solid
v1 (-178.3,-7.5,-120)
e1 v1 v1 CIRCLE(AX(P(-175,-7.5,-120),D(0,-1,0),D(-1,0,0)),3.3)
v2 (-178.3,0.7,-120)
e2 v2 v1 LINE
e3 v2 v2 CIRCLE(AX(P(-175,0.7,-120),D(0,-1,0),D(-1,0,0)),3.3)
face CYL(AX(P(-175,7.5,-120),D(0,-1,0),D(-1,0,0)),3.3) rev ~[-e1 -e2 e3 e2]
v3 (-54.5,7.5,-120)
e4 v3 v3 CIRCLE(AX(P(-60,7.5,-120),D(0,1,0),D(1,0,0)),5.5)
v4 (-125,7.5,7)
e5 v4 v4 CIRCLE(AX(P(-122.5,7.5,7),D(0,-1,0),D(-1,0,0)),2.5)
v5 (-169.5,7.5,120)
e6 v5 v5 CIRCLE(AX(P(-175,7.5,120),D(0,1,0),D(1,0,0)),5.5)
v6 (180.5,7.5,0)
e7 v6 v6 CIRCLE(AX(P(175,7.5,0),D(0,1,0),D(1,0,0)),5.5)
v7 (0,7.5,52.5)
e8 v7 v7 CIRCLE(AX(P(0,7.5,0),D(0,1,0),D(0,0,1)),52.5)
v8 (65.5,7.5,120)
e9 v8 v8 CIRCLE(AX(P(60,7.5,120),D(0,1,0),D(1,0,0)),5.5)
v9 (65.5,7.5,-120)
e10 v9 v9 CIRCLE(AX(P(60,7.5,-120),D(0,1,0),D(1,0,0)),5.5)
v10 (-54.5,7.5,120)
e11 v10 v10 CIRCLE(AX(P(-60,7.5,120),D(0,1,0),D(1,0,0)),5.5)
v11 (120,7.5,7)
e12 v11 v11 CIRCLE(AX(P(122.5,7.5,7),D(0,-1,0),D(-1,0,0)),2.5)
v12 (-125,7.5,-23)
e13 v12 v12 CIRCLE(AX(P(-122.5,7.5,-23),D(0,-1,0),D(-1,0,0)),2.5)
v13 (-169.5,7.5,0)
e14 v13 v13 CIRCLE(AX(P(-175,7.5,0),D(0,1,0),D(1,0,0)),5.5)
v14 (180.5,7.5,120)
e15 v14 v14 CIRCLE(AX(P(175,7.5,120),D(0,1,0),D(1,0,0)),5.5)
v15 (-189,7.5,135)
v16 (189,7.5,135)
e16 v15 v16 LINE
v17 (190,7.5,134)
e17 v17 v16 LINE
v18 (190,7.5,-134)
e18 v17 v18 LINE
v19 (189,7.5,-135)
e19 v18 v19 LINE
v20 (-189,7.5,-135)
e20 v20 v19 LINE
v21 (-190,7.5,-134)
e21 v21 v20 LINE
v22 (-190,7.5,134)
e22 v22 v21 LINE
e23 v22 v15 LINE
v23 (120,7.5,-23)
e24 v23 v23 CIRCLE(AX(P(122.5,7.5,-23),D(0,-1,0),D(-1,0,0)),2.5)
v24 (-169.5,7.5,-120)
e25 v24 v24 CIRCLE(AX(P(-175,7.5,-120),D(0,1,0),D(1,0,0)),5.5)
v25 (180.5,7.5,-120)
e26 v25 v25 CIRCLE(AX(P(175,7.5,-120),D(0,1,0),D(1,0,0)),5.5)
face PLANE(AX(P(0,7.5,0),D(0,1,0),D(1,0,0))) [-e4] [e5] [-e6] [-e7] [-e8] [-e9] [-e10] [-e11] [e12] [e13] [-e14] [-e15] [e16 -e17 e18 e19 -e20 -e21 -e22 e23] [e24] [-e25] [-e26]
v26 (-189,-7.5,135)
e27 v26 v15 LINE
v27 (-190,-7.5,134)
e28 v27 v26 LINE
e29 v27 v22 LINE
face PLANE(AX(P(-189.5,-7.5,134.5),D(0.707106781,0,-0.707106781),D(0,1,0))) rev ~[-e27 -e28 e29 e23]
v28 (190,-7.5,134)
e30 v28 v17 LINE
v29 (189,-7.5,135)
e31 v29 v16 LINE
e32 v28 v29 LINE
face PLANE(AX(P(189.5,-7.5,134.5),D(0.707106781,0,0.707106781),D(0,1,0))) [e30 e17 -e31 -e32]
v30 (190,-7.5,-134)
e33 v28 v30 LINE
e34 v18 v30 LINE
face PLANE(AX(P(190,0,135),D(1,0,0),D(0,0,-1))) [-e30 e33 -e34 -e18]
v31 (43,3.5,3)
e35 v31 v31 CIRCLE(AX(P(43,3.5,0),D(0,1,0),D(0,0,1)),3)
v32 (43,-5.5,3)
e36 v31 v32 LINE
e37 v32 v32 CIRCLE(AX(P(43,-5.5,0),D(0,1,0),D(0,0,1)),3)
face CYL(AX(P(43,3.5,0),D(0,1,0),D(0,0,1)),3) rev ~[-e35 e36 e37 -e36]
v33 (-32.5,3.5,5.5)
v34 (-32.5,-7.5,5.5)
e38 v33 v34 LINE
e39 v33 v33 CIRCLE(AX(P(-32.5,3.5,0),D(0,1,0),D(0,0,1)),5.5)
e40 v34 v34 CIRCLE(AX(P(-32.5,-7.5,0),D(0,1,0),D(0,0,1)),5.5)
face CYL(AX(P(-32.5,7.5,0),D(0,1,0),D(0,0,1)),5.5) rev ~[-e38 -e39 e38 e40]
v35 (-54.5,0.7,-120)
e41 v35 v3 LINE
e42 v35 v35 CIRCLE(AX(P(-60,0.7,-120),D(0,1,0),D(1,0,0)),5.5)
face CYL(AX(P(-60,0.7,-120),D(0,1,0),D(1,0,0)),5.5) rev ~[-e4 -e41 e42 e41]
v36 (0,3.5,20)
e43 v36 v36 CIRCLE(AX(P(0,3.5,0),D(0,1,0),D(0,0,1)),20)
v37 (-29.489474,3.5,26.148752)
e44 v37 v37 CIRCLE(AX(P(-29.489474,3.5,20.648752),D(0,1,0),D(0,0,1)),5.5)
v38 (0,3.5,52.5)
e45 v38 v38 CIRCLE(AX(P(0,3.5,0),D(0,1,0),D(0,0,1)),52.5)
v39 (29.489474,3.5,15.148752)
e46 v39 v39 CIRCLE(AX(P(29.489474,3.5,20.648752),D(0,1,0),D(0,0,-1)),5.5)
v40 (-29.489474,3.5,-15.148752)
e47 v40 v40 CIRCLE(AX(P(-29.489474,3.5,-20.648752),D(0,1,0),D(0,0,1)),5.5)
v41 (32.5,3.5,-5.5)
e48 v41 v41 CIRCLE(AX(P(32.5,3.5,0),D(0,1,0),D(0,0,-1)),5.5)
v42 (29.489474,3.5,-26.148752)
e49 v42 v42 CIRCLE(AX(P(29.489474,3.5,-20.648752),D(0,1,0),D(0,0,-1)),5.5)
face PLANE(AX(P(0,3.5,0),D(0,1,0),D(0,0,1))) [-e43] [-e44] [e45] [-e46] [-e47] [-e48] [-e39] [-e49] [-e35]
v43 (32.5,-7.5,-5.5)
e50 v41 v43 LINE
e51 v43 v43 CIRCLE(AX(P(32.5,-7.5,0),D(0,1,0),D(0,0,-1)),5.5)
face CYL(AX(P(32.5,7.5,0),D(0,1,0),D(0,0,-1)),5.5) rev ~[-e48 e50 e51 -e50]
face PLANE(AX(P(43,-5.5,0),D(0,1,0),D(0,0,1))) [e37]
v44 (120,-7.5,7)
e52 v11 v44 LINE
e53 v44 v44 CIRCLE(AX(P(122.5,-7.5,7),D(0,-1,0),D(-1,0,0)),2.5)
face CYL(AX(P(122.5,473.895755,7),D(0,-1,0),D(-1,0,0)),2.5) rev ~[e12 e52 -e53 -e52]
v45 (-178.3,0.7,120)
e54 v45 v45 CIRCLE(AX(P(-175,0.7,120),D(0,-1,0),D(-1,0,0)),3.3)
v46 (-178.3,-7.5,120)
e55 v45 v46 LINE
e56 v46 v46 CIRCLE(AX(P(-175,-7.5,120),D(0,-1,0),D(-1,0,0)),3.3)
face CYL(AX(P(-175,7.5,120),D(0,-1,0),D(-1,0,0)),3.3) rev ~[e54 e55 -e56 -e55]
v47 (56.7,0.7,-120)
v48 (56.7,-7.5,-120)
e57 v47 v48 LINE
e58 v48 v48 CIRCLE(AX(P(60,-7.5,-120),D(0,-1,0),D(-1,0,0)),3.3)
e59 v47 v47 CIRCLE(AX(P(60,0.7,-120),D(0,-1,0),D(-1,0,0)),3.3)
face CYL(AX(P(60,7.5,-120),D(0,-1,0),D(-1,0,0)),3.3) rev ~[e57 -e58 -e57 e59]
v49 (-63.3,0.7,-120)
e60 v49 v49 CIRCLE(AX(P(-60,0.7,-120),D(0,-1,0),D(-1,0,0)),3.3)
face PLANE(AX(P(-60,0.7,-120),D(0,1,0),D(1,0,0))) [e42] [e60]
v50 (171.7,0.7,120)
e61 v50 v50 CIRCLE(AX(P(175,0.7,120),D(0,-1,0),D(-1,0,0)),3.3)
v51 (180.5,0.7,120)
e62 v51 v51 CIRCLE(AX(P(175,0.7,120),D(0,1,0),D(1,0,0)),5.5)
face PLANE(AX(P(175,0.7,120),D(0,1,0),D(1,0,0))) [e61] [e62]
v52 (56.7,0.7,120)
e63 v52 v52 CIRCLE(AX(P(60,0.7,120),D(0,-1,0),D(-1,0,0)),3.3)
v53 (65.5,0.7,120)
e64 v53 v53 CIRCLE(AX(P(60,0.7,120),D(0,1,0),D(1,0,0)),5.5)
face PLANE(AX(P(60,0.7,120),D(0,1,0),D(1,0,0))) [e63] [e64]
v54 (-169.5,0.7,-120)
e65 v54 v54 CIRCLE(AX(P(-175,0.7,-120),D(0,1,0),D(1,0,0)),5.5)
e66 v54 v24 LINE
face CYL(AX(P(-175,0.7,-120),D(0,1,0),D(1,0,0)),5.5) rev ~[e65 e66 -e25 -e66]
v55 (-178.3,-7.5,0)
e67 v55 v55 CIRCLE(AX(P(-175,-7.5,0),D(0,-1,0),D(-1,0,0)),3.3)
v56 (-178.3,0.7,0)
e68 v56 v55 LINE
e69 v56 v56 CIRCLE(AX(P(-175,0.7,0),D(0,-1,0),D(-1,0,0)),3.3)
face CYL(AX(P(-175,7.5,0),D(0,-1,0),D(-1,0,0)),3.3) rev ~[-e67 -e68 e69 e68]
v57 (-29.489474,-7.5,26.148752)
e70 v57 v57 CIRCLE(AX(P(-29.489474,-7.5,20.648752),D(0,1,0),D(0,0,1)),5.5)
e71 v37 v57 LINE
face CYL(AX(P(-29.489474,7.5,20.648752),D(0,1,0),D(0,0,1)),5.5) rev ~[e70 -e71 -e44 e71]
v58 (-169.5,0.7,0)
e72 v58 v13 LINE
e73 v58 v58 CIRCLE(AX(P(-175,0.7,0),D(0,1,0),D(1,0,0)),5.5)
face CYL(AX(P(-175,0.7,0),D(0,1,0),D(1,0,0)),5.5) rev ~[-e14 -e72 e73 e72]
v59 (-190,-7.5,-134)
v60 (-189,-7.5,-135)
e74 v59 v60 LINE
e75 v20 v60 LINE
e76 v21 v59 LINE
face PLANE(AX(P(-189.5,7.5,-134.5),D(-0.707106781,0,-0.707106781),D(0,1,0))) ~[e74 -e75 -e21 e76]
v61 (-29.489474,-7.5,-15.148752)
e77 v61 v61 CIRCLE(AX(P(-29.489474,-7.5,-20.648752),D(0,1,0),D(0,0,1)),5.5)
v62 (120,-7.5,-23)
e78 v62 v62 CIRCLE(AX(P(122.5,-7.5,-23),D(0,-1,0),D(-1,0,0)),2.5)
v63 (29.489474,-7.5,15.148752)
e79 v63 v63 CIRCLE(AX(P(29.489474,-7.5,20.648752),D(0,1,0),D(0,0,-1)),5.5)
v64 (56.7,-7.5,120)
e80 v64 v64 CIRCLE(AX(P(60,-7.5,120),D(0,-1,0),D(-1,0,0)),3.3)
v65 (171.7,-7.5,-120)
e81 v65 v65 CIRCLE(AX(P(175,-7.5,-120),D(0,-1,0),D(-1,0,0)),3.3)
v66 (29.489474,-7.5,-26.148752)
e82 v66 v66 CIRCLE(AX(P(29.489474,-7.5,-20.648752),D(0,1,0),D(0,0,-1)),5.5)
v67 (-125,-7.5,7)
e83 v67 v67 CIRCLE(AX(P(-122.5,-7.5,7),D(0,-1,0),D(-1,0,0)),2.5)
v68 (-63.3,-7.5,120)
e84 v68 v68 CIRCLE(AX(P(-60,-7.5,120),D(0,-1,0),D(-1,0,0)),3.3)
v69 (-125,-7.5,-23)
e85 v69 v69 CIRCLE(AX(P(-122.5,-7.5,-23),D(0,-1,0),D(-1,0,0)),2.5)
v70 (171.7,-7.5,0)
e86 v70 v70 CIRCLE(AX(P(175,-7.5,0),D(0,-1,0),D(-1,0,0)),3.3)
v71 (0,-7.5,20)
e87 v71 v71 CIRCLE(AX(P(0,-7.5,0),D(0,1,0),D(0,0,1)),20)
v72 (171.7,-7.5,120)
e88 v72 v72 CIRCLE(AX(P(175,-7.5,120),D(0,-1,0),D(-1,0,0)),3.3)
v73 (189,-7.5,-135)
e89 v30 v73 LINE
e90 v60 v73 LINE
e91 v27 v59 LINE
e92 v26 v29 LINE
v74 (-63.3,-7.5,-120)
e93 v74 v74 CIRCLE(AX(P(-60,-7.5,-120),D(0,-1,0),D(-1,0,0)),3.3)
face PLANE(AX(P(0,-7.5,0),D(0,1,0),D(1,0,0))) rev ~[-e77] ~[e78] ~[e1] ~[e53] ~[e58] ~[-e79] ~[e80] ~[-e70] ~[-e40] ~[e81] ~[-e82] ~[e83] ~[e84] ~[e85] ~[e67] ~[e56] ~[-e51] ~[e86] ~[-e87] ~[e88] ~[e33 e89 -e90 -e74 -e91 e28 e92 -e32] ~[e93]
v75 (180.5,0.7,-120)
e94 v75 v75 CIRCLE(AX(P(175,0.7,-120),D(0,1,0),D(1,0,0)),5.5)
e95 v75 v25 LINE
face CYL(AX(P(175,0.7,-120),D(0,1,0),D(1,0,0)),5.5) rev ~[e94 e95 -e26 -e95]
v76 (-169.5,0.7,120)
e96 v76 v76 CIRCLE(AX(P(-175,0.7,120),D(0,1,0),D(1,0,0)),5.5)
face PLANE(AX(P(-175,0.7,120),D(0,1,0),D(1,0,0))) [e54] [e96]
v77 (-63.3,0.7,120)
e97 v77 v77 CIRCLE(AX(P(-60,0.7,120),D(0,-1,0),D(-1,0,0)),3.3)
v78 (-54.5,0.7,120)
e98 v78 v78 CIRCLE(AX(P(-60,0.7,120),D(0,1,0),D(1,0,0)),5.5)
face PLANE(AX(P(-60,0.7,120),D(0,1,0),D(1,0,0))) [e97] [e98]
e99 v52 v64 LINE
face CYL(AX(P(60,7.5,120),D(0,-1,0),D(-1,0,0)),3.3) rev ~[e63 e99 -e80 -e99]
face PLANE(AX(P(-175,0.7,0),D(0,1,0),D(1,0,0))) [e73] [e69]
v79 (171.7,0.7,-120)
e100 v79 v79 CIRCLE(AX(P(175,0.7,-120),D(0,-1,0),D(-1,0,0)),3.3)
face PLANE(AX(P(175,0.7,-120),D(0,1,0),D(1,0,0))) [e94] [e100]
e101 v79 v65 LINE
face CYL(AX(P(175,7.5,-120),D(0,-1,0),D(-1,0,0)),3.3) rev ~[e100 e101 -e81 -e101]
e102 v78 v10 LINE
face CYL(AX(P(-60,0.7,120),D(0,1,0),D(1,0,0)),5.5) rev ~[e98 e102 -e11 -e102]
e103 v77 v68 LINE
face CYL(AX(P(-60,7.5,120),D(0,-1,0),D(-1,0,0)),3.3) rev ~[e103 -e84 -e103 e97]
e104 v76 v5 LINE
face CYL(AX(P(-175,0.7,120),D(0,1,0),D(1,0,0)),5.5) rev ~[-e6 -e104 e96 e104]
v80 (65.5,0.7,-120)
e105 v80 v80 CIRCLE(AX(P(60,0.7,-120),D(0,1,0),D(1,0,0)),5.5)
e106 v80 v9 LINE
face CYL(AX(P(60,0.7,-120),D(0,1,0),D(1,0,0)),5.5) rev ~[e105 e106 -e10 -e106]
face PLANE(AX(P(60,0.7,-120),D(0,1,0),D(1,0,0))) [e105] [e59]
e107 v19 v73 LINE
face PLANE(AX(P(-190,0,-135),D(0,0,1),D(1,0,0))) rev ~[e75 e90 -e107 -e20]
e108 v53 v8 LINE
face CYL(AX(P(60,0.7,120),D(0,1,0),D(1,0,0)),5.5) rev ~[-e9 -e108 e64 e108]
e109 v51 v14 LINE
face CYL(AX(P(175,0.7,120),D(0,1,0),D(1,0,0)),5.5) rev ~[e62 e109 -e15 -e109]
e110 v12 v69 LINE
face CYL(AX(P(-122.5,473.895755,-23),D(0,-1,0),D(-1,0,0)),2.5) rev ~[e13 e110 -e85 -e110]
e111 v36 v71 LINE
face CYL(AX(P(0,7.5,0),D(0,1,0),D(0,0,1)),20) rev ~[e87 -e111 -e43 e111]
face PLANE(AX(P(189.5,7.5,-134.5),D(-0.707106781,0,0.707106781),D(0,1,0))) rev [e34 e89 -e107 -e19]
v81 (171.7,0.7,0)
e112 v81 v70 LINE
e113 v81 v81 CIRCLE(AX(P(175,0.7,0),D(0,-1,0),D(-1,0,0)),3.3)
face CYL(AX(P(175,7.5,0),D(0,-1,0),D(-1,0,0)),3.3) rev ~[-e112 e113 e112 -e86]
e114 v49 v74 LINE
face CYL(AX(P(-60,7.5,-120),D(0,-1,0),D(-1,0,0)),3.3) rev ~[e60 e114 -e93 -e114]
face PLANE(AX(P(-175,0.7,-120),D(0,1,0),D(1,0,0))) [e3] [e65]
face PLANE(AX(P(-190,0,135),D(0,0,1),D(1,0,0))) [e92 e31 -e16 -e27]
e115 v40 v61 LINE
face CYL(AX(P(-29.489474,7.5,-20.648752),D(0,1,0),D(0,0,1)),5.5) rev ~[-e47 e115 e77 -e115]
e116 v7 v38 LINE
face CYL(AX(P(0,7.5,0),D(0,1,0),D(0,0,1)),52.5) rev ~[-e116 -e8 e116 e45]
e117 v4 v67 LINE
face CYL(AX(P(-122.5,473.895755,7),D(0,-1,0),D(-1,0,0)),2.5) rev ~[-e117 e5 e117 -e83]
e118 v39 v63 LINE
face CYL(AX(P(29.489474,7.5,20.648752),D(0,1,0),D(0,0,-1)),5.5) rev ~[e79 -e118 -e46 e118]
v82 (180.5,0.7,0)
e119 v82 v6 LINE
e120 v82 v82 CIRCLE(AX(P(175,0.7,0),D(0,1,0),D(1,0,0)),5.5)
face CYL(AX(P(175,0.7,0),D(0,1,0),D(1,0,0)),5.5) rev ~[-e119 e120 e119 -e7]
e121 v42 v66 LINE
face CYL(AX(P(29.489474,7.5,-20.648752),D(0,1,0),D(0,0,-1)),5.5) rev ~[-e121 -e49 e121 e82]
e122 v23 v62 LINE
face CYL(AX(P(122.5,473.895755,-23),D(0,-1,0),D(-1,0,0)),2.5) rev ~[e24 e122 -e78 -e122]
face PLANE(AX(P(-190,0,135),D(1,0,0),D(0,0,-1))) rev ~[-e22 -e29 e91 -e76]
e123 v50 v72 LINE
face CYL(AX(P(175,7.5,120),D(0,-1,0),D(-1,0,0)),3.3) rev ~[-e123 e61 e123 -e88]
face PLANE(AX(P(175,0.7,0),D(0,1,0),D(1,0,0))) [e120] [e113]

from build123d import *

# Parameters (mm, degrees)
SKETCH_1_W                = 380
SKETCH_1_H                = 270
EXTRUDE_1_DEPTH           = 7.5
CHAMFER_1_SIZE            = 1
SKETCH_2_R                = 20
CUT_EXTRUDE_1_DEPTH       = 15
HOLE_WIZARD_3_D           = 6.6
HOLE_WIZARD_3_CBORE_D     = 11
HOLE_WIZARD_3_CBORE_DEPTH = 6.8
SKETCH_9_R                = 5.5
CUT_EXTRUDE_2_DEPTH       = 234.559414283
SKETCH_11_R               = 52.5
CUT_EXTRUDE_3_DEPTH       = 4
HOLE_WIZARD_M6_1_D        = 5
SKETCH_15_R               = 3
CUT_EXTRUDE_4_DEPTH       = 9


with BuildPart() as part:
    # 草图1 → 凸台-拉伸1 (new, symmetric)
    with BuildSketch(Plane(origin=(0, 0, 0), x_dir=(1, 0, 0), z_dir=(0, 1, 0))):
        Rectangle(SKETCH_1_W, SKETCH_1_H)
    extrude(amount=EXTRUDE_1_DEPTH, both=True)

    # 倒角1
    chamfer_1_edges = [part.edges().sort_by_distance(p)[0] for p in [
        (190, 0, 135),
        (-190, 0, 135),
        (-190, 0, -135),
        (190, 0, -135),
    ]]
    chamfer(chamfer_1_edges, length=CHAMFER_1_SIZE)

    # 草图2 → 切除-拉伸1 (cut)
    with BuildSketch(Plane(origin=(0, 7.5, 0), x_dir=(1, 0, 0), z_dir=(0, 1, 0))):
        with Locations(Location((0, 0, 0), (0, 0, 270))):
            Circle(SKETCH_2_R)
    extrude(amount=-CUT_EXTRUDE_1_DEPTH, mode=Mode.SUBTRACT)

    # 打孔尺寸(%根据)内六角圆柱头螺钉的类型3 (through all)
    with Locations(Plane(origin=(0, 7.5, 0), x_dir=(1, 0, 0), z_dir=(0, 1, 0))):
        with Locations((-175, 120), (-60, 120), (-60, -120), (-175, 0), (-175, -120), (175, -120), (175, 0), (60, -120), (60, 120), (175, 120)):
            CounterBoreHole(HOLE_WIZARD_3_D / 2, HOLE_WIZARD_3_CBORE_D / 2, HOLE_WIZARD_3_CBORE_DEPTH)

    # 草图9 → 切除-拉伸2 (cut, through all)
    with BuildSketch(Plane(origin=(0, 7.5, 0), x_dir=(1, 0, 0), z_dir=(0, 1, 0))):
        with Locations(Location((-29.489473594, 20.648751709, 0), (0, 0, 270))):
            Circle(SKETCH_9_R)
        with Locations(Location((-29.489473594, -20.648751709, 0), (0, 0, 270))):
            Circle(SKETCH_9_R)
        with Locations(Location((-32.5, 0, 0), (0, 0, 270))):
            Circle(SKETCH_9_R)
        with Locations(Location((29.489473594, -20.648751709, 0), (0, 0, 90))):
            Circle(SKETCH_9_R)
        with Locations(Location((32.5, 0, 0), (0, 0, 90))):
            Circle(SKETCH_9_R)
        with Locations(Location((29.489473594, 20.648751709, 0), (0, 0, 90))):
            Circle(SKETCH_9_R)
    extrude(amount=-CUT_EXTRUDE_2_DEPTH, mode=Mode.SUBTRACT)

    # 草图11 → 切除-拉伸3 (cut)
    with BuildSketch(Plane(origin=(0, 7.5, 0), x_dir=(1, 0, 0), z_dir=(0, 1, 0))):
        with Locations(Location((0, 0, 0), (0, 0, 270))):
            Circle(SKETCH_11_R)
    extrude(amount=-CUT_EXTRUDE_3_DEPTH, mode=Mode.SUBTRACT)

    # M6 螺纹孔1 (through all)
    with Locations(Plane(origin=(0, 7.5, 0), x_dir=(1, 0, 0), z_dir=(0, 1, 0))):
        with Locations((122.5, -7), (122.5, 23), (-122.5, 23), (-122.5, -7)):
            Hole(HOLE_WIZARD_M6_1_D / 2)

    # 草图15 → 切除-拉伸4 (cut)
    with BuildSketch(Plane(origin=(0, 3.5, 0), x_dir=(1, 0, 0), z_dir=(0, 1, 0))):
        with Locations(Location((43, 0, 0), (0, 0, 270))):
            Circle(SKETCH_15_R)
    extrude(amount=-CUT_EXTRUDE_4_DEPTH, mode=Mode.SUBTRACT)


solid = part.part
